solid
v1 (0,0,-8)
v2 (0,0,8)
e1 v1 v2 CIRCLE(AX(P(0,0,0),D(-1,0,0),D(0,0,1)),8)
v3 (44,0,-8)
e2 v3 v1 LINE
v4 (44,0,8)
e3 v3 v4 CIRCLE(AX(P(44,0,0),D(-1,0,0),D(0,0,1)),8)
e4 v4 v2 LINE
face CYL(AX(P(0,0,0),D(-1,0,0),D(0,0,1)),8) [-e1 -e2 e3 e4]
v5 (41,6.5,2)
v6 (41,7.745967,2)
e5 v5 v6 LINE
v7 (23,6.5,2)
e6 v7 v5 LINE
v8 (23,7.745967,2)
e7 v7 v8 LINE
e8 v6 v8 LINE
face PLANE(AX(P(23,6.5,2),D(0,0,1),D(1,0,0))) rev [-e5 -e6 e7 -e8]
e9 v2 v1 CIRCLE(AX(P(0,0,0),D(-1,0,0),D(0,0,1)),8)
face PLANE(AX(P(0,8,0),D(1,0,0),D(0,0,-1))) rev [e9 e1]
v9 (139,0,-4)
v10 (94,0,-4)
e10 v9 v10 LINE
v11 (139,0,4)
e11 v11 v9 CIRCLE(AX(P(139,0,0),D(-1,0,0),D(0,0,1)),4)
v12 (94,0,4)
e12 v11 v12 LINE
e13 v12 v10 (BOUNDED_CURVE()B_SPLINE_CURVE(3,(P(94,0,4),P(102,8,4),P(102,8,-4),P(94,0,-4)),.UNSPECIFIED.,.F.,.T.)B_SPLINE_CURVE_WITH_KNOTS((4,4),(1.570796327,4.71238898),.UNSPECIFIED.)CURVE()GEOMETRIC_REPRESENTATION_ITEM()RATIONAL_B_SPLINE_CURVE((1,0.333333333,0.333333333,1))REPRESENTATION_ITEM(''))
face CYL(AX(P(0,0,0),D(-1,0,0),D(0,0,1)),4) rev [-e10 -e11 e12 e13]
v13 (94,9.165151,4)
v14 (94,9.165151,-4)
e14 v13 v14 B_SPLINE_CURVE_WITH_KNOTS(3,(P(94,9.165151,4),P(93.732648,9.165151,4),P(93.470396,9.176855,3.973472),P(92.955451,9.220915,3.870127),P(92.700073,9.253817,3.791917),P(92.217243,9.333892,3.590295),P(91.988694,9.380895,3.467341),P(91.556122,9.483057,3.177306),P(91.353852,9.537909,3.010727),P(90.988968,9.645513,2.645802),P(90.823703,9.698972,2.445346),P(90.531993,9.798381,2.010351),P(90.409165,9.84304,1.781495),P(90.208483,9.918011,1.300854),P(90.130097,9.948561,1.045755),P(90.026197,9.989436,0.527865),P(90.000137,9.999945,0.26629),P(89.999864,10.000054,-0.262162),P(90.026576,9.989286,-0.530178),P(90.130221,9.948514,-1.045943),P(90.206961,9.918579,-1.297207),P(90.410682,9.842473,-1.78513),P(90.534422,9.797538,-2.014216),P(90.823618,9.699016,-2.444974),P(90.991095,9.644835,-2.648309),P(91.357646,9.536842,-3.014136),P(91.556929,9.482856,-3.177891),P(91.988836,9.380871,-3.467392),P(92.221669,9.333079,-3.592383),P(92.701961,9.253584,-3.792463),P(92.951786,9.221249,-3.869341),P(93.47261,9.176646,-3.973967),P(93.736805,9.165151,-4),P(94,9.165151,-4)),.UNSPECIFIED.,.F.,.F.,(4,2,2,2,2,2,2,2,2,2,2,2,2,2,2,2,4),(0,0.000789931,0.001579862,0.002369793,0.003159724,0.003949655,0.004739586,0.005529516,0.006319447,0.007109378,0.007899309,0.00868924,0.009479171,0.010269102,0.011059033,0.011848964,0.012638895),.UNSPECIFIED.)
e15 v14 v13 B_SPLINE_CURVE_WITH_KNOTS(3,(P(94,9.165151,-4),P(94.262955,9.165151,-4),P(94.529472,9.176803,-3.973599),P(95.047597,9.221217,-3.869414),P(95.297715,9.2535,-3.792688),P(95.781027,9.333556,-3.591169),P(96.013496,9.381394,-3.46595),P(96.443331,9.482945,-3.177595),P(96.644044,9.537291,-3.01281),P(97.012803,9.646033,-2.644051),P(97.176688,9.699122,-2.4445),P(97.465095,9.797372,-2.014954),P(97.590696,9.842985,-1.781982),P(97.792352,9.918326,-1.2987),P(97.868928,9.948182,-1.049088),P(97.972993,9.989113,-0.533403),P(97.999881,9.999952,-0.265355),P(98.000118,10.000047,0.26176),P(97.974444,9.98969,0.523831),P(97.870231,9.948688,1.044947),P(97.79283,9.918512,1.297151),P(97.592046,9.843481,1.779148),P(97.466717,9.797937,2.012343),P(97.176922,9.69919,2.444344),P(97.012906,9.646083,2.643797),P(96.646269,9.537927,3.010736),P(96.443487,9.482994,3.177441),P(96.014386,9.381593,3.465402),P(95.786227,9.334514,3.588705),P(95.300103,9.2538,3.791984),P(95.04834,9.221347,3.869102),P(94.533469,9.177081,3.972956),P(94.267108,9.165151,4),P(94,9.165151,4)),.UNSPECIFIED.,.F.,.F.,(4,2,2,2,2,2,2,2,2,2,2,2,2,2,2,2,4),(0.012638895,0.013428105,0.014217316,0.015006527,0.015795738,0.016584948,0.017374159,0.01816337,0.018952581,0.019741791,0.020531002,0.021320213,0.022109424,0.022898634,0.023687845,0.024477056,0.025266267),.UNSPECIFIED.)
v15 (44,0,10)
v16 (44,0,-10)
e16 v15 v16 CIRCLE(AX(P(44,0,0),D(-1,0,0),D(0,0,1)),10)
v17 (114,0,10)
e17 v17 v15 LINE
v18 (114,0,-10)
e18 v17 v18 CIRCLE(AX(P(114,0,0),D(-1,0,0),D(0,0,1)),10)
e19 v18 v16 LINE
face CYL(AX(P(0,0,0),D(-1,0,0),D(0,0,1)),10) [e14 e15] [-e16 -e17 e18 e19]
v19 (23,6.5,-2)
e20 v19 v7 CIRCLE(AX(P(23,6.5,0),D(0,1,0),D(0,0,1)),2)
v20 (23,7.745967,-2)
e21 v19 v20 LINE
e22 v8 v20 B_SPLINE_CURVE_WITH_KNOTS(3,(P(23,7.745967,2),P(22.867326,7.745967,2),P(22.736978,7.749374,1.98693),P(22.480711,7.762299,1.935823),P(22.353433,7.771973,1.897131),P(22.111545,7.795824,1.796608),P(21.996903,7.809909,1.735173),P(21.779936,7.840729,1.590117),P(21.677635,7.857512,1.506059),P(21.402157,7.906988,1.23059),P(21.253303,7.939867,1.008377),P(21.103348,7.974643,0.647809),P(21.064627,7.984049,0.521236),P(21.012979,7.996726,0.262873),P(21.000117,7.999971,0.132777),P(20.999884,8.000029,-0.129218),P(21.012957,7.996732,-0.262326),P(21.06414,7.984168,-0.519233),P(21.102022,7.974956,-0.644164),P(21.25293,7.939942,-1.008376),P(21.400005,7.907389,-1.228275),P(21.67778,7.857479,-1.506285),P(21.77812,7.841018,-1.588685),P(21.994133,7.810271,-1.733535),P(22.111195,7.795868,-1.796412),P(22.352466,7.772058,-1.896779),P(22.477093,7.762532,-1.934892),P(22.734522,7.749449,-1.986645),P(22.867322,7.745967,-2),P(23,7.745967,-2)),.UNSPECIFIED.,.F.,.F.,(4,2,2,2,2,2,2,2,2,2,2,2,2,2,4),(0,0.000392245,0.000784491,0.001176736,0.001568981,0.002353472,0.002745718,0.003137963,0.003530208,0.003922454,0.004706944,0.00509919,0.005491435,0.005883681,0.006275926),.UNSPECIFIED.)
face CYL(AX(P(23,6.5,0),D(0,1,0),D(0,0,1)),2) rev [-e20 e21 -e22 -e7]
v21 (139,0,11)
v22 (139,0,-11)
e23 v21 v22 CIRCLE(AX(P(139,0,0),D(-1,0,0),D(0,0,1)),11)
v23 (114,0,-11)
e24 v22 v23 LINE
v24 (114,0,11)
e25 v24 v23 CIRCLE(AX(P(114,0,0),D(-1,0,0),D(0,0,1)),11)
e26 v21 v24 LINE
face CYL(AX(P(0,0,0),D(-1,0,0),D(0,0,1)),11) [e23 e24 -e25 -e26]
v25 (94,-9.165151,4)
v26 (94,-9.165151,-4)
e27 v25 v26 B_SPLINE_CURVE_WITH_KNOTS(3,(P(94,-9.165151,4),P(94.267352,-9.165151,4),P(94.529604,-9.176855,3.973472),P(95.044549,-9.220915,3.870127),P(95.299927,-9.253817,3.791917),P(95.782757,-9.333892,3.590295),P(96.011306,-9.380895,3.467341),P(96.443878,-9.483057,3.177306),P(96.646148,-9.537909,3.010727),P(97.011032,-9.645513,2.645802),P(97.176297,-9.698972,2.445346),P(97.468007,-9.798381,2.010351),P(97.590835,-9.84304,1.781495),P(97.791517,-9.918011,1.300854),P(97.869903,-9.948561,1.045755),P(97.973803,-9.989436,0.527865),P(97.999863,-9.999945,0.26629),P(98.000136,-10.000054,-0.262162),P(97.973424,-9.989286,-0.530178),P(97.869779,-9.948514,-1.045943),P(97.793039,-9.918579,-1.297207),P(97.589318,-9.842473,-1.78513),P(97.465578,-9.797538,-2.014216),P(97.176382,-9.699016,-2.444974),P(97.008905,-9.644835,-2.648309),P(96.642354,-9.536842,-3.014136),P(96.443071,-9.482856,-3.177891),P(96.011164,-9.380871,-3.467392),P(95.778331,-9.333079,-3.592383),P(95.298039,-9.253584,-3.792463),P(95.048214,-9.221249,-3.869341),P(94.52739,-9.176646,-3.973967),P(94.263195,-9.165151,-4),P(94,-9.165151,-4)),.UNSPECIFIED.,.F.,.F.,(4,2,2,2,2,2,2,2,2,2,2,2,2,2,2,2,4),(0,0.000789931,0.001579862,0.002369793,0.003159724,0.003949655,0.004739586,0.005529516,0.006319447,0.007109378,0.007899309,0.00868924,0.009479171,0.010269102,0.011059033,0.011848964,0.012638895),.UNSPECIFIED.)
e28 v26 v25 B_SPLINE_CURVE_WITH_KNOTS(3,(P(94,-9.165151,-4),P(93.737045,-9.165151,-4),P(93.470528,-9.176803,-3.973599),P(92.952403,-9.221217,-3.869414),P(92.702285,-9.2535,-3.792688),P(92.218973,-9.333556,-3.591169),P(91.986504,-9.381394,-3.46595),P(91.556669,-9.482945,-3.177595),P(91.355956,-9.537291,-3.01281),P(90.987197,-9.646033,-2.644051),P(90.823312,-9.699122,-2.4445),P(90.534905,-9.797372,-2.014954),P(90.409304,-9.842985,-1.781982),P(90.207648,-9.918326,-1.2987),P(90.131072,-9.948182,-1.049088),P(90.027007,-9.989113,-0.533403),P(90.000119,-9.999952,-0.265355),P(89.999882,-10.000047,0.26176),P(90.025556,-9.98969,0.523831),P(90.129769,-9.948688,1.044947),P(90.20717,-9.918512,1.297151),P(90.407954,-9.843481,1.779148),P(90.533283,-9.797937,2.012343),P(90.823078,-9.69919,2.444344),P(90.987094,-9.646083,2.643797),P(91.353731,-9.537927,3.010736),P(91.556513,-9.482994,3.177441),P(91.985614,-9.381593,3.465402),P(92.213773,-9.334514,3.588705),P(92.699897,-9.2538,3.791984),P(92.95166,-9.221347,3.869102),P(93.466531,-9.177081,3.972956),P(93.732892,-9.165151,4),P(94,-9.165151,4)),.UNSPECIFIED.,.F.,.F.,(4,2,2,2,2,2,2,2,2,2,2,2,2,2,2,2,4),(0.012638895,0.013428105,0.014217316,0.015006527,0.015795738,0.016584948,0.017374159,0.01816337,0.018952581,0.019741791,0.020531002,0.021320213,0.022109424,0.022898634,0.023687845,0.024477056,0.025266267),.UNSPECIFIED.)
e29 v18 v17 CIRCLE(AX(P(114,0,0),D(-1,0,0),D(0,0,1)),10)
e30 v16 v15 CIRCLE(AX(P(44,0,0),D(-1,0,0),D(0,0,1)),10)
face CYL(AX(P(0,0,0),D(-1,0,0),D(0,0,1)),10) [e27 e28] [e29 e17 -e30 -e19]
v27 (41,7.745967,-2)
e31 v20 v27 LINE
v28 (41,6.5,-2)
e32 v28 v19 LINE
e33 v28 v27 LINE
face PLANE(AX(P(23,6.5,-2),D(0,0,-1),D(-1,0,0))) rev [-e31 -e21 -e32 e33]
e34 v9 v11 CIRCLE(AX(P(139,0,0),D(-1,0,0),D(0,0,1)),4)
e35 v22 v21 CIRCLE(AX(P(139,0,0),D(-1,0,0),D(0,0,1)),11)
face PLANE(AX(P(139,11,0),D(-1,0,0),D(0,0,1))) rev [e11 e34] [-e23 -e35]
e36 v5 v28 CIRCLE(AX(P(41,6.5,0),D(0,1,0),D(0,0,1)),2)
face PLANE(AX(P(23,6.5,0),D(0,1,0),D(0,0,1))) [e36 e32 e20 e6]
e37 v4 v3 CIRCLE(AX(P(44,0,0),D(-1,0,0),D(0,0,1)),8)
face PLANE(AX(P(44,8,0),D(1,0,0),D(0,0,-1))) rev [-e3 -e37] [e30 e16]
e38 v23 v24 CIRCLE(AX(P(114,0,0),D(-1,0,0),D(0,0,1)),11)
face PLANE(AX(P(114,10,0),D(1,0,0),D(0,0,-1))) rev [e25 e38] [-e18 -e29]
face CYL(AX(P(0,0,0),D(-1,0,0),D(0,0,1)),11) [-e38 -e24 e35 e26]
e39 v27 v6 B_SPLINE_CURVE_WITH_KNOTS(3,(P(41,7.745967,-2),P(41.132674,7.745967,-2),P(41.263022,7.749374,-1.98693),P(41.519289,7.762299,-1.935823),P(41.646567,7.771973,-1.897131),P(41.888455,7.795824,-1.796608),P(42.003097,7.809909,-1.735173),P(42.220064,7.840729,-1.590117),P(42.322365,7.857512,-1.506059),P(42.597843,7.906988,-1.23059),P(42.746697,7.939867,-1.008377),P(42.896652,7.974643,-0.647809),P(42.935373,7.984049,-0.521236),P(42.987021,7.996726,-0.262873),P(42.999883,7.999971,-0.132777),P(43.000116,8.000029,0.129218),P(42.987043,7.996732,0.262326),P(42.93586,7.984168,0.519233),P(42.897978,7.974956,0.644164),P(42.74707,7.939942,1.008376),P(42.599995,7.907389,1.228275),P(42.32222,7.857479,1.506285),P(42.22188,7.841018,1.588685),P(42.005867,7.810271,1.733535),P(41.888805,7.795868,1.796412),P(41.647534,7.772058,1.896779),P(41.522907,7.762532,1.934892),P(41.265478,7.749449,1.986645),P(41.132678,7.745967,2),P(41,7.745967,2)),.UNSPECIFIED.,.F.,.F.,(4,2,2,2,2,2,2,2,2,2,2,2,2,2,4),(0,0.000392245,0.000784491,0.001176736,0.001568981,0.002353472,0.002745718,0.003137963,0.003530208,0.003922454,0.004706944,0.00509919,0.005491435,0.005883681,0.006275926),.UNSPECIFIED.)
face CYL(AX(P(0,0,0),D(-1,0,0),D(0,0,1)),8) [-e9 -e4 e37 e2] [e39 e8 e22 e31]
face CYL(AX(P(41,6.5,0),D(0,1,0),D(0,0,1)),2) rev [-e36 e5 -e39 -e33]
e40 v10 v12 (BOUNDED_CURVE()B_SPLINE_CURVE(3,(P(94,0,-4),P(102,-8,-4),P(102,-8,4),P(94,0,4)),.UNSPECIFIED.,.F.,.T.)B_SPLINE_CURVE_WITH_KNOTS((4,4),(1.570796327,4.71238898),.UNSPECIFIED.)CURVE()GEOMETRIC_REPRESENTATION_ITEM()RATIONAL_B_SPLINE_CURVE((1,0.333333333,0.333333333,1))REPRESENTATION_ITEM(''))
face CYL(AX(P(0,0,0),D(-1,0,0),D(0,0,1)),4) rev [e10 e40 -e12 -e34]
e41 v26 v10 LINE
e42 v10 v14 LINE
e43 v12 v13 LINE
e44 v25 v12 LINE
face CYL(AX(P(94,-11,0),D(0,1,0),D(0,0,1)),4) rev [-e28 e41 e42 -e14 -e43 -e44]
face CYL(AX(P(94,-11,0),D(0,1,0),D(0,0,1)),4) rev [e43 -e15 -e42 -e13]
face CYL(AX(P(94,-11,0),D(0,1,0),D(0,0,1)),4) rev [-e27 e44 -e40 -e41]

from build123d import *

# Parameters (mm, degrees)
CUT_EXTRUDE1_START      = 8
CUT_EXTRUDE1_DEPTH      = 1.5
CUT_EXTRUDE2_DEPTH      = 140.867794721
CUT_EXTRUDE2_DEPTH_BACK = 140.867794721
SKETCH3_R               = 4


with BuildPart() as part:
    # Sketch1 → Revolve2 (revolve)
    with BuildSketch(Plane.XY, mode=Mode.PRIVATE) as revolve2_sk:
        Polygon((0, 8), (44, 8), (44, 10), (114, 10), (114, 11), (139, 11), (139, 4), (94, 4), (94, 0), (0, 0), align=None)
    revolve(revolve2_sk.sketch.rotate(Axis((0, 0, 0), (1, 0, 0)), 90), axis=Axis((0, 0, 0), (1, 0, 0)))

    # Sketch2 → Cut-Extrude1 (cut)
    with BuildSketch(Plane(origin=(0, 0, 0), x_dir=(1, 0, 0), z_dir=(0, 1, 0)).offset(CUT_EXTRUDE1_START)):
        with BuildLine():
            Line((23, 2), (41, 2))
            ThreePointArc((41, 2), (43, 0), (41, -2))
            Line((41, -2), (23, -2))
            ThreePointArc((23, -2), (21, 0), (23, 2))
        make_face()
    extrude(amount=-CUT_EXTRUDE1_DEPTH, mode=Mode.SUBTRACT)

    # Sketch3 → Cut-Extrude2 (cut, two sides: drawn at the far end of the back side and taken through both)
    with BuildSketch(Plane(origin=(0, 0, 0), x_dir=(1, 0, 0), z_dir=(0, 1, 0)).offset(-CUT_EXTRUDE2_DEPTH_BACK)):
        with Locations(Location((94, 0, 0), (0, 0, 270))):
            Circle(SKETCH3_R)
    extrude(amount=CUT_EXTRUDE2_DEPTH + CUT_EXTRUDE2_DEPTH_BACK, mode=Mode.SUBTRACT)


solid = part.part
